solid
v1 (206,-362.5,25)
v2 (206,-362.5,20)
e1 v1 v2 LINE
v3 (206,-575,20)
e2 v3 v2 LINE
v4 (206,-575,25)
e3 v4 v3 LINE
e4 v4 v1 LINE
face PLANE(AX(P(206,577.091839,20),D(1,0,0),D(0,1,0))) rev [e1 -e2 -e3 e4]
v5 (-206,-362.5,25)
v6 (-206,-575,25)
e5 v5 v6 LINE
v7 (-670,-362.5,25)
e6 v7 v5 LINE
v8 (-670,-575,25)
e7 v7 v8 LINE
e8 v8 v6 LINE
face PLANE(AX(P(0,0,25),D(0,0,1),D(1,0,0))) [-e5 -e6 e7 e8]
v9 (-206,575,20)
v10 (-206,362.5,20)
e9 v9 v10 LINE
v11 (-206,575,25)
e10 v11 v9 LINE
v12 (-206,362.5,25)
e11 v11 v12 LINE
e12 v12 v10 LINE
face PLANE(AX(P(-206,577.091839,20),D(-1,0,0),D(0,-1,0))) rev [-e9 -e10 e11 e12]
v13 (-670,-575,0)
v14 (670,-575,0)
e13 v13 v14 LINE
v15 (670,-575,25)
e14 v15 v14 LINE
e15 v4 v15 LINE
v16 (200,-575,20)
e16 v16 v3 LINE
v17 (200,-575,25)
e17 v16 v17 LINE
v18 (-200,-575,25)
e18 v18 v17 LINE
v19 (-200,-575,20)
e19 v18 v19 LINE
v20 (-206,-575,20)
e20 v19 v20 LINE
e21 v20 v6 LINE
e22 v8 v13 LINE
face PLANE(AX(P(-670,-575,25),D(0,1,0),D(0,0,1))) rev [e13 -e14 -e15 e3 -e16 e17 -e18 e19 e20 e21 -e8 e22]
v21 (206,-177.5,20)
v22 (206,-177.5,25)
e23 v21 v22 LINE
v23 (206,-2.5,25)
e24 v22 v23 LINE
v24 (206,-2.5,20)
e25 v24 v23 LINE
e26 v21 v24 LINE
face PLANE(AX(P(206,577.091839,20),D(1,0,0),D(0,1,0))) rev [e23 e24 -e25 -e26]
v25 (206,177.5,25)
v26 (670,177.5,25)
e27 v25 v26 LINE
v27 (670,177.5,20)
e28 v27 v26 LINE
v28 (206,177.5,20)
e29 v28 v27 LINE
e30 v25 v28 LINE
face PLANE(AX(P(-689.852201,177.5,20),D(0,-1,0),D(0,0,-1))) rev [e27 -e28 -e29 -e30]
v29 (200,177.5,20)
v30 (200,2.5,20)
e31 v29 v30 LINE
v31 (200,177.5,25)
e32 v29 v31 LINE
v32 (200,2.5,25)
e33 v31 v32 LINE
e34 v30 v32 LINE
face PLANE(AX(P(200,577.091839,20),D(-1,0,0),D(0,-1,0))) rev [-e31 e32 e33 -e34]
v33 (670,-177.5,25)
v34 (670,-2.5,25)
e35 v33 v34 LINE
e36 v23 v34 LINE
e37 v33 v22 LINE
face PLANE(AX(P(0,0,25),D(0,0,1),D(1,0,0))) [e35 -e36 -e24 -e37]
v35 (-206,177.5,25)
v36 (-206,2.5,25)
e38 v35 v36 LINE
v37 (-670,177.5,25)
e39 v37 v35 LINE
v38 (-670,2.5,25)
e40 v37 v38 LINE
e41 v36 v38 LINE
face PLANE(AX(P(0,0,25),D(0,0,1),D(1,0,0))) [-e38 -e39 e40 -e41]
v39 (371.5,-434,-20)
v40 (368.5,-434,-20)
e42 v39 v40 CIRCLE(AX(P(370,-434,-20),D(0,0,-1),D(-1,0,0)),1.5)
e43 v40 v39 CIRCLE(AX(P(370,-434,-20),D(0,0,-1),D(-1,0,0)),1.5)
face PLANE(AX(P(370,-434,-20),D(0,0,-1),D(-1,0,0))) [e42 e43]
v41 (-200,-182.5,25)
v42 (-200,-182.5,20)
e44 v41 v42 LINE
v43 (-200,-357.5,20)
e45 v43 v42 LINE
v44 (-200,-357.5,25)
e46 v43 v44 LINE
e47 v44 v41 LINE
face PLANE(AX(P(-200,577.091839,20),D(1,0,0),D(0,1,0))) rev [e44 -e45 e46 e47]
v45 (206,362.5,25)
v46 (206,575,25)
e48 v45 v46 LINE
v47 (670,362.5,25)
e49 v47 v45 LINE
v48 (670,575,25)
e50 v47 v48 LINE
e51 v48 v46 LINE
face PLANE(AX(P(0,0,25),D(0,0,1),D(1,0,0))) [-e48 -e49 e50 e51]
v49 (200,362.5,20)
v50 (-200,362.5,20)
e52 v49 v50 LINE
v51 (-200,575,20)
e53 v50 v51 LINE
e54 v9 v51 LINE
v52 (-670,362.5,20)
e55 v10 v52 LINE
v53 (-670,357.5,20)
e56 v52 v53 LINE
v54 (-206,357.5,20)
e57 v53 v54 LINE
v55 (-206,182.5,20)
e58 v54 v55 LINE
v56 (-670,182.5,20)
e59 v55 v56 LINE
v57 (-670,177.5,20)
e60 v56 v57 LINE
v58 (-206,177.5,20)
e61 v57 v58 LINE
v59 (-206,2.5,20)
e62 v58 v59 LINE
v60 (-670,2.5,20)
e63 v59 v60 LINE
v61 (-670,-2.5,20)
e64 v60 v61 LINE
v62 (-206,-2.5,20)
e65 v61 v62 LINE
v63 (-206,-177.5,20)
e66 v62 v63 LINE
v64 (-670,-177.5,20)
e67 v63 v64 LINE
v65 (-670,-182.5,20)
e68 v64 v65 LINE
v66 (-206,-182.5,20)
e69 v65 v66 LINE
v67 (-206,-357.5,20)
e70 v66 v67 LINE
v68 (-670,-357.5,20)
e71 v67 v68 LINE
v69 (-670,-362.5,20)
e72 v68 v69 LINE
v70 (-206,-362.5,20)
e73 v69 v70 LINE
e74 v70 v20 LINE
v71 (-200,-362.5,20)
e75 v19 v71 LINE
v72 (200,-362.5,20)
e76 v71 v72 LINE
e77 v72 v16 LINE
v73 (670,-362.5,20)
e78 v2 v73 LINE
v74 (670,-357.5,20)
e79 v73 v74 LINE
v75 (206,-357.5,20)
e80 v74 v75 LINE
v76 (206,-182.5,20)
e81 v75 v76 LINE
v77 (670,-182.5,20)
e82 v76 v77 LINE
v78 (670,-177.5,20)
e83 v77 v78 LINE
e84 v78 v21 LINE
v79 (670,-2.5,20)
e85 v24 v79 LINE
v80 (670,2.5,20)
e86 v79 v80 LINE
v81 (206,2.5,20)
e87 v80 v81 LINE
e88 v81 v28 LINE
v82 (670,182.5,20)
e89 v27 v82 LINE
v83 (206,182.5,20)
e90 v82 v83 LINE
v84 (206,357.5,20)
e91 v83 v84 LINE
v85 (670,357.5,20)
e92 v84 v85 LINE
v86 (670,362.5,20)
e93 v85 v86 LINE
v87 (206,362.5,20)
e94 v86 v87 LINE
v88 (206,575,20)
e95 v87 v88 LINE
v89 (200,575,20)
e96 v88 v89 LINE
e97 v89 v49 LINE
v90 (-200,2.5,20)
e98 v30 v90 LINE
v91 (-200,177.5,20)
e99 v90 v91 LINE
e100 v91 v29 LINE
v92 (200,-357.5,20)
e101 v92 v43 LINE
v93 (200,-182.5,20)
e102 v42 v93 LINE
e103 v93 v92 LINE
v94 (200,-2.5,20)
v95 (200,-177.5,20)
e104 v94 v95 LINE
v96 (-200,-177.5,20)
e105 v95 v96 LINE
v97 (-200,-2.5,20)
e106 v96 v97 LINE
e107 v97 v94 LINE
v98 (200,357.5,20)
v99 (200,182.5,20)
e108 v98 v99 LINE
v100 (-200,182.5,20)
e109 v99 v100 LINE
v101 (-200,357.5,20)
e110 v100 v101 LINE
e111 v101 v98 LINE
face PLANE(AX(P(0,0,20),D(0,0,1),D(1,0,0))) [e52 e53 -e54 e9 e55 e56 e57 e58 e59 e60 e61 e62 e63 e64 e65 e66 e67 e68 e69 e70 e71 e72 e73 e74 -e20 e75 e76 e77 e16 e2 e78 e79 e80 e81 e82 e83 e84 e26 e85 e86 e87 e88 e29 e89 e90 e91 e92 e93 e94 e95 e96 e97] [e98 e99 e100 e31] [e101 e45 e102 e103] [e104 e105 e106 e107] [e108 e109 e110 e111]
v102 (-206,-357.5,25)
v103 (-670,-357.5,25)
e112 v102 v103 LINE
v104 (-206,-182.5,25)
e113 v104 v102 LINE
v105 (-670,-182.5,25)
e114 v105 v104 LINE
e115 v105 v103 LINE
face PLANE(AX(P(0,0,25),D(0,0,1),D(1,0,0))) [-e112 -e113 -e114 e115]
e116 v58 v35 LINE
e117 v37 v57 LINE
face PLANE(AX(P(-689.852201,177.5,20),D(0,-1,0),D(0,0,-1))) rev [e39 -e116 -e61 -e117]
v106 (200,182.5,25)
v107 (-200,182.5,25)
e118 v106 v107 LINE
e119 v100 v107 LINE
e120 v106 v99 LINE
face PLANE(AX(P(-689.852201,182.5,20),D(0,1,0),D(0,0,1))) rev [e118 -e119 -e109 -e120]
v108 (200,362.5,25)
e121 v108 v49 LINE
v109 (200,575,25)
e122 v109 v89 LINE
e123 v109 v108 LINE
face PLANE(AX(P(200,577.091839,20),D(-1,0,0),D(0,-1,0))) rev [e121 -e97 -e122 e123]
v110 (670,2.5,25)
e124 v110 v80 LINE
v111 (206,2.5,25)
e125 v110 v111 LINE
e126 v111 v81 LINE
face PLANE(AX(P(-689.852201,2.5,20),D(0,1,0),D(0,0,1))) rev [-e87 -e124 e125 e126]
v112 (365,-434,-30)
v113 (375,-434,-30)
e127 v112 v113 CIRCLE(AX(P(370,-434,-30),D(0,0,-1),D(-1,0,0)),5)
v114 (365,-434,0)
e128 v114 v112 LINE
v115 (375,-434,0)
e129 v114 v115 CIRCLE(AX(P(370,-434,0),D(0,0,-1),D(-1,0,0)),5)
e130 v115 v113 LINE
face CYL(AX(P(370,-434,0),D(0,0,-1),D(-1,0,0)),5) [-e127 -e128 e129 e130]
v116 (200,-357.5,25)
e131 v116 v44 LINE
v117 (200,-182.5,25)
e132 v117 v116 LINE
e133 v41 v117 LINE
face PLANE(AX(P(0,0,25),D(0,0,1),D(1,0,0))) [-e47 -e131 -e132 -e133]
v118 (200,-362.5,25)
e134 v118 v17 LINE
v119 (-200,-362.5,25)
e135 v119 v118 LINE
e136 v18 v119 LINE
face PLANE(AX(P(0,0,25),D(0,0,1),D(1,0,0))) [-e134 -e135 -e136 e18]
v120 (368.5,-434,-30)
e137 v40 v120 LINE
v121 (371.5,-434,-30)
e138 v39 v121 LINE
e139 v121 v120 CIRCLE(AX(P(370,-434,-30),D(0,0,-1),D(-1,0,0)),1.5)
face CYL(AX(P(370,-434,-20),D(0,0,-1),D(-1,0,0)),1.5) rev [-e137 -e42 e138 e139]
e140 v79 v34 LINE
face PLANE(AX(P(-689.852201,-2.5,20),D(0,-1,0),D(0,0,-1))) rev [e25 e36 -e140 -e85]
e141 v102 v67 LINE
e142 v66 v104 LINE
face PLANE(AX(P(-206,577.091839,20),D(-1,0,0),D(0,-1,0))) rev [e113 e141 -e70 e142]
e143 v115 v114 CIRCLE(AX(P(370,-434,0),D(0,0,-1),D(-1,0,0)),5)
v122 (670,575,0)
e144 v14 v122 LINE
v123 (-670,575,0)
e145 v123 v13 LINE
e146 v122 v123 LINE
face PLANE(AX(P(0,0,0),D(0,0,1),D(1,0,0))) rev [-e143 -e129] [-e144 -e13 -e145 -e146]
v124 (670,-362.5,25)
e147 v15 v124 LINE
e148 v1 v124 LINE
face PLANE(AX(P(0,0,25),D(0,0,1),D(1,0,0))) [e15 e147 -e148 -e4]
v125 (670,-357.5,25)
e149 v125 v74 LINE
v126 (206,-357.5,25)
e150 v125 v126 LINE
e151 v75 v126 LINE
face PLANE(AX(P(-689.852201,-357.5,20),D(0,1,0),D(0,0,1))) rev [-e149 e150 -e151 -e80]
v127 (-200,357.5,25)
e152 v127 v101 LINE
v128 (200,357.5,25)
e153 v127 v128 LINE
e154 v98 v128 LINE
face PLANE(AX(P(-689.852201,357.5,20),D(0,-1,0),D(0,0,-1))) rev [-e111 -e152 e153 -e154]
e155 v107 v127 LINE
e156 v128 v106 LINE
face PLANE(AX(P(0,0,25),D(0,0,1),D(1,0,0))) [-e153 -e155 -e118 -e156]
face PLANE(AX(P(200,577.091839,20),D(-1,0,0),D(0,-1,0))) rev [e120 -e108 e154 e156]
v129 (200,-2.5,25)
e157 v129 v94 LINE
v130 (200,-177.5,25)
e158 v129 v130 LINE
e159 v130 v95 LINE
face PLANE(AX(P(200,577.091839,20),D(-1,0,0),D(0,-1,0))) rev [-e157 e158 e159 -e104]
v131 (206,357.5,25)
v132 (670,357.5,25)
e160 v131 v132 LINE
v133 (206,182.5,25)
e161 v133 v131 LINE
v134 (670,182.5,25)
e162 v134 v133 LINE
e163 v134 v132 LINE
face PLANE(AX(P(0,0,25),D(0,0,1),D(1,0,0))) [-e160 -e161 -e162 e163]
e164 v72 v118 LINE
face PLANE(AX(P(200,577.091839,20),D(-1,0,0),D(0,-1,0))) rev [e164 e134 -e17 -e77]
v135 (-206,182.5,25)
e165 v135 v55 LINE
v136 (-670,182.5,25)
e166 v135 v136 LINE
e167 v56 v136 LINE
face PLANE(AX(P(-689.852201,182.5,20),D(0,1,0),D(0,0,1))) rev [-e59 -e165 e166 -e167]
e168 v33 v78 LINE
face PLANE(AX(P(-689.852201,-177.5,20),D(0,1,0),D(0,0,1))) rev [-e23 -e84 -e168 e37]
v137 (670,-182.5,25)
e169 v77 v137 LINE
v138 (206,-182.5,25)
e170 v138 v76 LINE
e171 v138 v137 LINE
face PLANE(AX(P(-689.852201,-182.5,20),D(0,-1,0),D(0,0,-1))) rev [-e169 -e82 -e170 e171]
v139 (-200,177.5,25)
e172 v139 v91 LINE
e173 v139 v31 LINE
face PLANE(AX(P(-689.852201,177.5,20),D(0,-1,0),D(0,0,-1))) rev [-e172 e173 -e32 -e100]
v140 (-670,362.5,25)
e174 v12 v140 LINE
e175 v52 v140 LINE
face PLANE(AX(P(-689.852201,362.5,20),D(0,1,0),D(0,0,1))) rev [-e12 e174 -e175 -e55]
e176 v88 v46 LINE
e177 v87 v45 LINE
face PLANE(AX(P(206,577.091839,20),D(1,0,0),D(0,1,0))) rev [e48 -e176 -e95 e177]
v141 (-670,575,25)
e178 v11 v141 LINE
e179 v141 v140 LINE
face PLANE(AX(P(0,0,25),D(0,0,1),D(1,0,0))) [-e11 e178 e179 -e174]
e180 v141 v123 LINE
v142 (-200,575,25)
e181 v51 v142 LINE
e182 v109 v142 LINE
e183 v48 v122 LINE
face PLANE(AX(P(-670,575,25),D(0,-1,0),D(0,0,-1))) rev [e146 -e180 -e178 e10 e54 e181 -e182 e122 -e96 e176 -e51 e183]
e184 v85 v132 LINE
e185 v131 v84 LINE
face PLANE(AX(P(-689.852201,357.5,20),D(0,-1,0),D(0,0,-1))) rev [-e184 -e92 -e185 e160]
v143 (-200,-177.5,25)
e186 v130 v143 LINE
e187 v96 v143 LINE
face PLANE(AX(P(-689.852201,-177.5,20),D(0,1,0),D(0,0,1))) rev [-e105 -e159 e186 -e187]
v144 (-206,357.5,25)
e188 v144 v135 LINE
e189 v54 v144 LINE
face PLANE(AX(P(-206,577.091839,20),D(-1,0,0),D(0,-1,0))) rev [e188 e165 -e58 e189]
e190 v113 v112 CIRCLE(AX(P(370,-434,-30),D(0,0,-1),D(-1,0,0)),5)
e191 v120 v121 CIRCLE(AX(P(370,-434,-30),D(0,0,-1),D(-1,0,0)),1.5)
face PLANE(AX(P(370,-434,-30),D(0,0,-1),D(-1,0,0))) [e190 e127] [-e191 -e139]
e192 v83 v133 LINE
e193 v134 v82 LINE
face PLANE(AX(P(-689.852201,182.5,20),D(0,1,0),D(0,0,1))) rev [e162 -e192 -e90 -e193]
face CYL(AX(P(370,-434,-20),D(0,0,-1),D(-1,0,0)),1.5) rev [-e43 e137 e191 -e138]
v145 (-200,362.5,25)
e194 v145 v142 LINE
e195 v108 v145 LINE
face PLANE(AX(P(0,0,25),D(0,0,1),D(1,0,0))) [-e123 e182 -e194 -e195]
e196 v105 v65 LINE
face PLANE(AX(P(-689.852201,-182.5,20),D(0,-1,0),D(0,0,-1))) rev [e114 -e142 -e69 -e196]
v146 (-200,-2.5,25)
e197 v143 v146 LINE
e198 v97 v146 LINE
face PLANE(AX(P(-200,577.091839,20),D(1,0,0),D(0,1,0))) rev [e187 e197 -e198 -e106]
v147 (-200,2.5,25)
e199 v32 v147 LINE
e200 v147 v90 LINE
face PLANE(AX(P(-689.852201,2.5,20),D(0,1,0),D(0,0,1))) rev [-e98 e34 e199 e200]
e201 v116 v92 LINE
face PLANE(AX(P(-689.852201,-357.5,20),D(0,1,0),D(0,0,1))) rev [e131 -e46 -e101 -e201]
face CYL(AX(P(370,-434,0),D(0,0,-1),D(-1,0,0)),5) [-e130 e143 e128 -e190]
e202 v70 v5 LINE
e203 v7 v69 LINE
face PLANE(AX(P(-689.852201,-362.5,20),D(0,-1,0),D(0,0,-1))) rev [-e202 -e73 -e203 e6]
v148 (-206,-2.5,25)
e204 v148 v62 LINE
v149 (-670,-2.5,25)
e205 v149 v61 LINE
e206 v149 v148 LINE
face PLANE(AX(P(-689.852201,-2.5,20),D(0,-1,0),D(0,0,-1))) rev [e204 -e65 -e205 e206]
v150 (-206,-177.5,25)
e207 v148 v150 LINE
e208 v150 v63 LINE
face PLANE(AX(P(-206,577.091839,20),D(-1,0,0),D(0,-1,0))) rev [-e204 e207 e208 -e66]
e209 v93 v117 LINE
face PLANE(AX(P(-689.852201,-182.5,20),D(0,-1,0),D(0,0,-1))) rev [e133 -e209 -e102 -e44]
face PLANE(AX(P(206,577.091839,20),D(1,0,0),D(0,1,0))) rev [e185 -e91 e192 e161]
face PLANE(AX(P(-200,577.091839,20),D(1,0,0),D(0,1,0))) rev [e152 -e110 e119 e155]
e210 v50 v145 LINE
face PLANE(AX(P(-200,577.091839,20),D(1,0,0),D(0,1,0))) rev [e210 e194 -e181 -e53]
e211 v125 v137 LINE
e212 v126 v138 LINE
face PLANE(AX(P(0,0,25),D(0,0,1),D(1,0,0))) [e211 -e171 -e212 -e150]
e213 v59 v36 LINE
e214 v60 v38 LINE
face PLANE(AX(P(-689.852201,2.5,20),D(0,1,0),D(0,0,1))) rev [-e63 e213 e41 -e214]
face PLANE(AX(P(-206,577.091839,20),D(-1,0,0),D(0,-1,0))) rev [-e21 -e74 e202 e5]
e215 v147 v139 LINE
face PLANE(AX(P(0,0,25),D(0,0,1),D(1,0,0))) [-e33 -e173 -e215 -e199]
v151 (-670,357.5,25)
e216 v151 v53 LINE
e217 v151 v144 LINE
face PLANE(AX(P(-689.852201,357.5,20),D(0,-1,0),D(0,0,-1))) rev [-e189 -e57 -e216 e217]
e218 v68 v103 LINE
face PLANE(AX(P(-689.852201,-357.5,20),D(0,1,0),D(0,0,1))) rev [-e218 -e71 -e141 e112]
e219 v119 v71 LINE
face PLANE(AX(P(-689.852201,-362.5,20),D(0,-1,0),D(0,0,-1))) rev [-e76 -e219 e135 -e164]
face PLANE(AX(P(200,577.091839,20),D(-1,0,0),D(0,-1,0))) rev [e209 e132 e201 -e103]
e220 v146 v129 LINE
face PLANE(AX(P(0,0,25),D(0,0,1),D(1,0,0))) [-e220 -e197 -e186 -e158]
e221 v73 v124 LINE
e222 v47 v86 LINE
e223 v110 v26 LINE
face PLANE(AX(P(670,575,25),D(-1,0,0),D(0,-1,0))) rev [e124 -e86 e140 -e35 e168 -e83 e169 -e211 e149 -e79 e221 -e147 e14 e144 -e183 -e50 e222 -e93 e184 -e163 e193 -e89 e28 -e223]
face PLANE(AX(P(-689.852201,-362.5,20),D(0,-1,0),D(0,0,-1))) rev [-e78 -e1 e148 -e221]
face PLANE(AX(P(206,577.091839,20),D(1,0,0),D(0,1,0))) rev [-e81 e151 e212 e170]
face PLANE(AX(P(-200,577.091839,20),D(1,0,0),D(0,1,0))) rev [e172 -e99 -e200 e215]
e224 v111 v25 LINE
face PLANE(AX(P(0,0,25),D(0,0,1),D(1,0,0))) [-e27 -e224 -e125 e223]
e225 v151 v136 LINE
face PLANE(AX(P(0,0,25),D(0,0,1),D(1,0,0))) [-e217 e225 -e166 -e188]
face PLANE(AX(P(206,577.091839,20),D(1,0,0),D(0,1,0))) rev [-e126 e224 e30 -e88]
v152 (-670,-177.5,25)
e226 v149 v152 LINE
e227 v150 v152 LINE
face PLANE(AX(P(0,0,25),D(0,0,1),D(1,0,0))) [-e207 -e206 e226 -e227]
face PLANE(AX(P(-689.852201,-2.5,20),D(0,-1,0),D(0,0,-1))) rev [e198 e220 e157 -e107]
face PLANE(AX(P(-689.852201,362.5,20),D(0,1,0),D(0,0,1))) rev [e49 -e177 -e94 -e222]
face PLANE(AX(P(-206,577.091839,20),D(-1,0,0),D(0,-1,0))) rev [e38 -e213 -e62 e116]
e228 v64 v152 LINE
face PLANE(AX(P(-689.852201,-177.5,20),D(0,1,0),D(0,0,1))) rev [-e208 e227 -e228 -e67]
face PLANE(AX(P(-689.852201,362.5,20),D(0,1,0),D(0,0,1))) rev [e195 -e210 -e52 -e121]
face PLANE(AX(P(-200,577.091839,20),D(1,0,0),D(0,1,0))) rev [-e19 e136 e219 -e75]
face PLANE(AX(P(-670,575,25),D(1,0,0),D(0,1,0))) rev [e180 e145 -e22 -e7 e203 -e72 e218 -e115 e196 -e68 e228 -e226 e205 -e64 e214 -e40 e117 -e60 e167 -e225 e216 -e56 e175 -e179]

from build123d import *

# Parameters (mm, degrees)
SKETCH1_W           = 1340
SKETCH1_H           = 1150
BOSS_EXTRUDE1_DEPTH = 25
SKETCH2_W           = 1379.704401218
SKETCH2_H           = 5
CUT_EXTRUDE1_DEPTH  = 5
SKETCH3_W           = 6
SKETCH3_H           = 1155.334708323
CUT_EXTRUDE2_DEPTH  = 5
LPATTERN1_COUNT     = 3
LPATTERN1_PITCH     = 180
LPATTERN1_COL_COUNT = 3
LPATTERN1_COL_PITCH = 180
SWEEP1_PROFILE_R    = 5
SKETCH13_R          = 1.5
CUT_EXTRUDE3_DEPTH  = 10


with BuildPart() as part:
    # Sketch1 → Boss-Extrude1 (new body)
    with BuildSketch(Plane.XY):
        Rectangle(SKETCH1_W, SKETCH1_H)
    extrude(amount=BOSS_EXTRUDE1_DEPTH)

    # Sketch2 → Cut-Extrude1 (cut)
    with BuildSketch(Plane.XY.offset(25)):
        Rectangle(SKETCH2_W, SKETCH2_H)
    cut_extrude1 = extrude(amount=-CUT_EXTRUDE1_DEPTH, mode=Mode.SUBTRACT)

    # Sketch3 → Cut-Extrude2 (cut)
    with BuildSketch(Plane.XY.offset(25)):
        with Locations((203, -0.575515136)):
            Rectangle(SKETCH3_W, SKETCH3_H)
        with Locations((-203, -0.575515136)):
            Rectangle(SKETCH3_W, SKETCH3_H)
    extrude(amount=-CUT_EXTRUDE2_DEPTH, mode=Mode.SUBTRACT)

    # LPattern1: Cut-Extrude1 ×3
    with Locations(*[(0, -i * LPATTERN1_PITCH, 0) for i in range(1, LPATTERN1_COUNT)]):
        add(cut_extrude1, mode=Mode.SUBTRACT)

    # LPattern1 col: Cut-Extrude1 ×3
    with Locations(*[(0, i * LPATTERN1_COL_PITCH, 0) for i in range(1, LPATTERN1_COL_COUNT)]):
        add(cut_extrude1, mode=Mode.SUBTRACT)

    # Sweep1: sweep along a path in Sketch4
    with BuildLine(Plane(origin=(-49.523696958, -434, -370.281312655), x_dir=(0.9899494936611666, 0, -0.14142135623730917), z_dir=(0, -1, 0))) as sweep1_path:
        Line((362.941585957, 425.889408172), (367.184226644, 396.190923362))
    # Sweep1 profile (on start of the path) → Sweep1 (sweep)
    with BuildSketch(Plane(origin=(370, -434, 0), x_dir=(-1, 0, 0), z_dir=(0, 0, -1))):
        Circle(SWEEP1_PROFILE_R)
    sweep(path=sweep1_path.line)

    # Sketch13 → Cut-Extrude3 (cut)
    with BuildSketch(Plane(origin=(0, 0, -30), x_dir=(-1, 0, 0), z_dir=(0, 0, -1))):
        with Locations((-370, -434)):
            Circle(SKETCH13_R)
    extrude(amount=-CUT_EXTRUDE3_DEPTH, mode=Mode.SUBTRACT)


solid = part.part
